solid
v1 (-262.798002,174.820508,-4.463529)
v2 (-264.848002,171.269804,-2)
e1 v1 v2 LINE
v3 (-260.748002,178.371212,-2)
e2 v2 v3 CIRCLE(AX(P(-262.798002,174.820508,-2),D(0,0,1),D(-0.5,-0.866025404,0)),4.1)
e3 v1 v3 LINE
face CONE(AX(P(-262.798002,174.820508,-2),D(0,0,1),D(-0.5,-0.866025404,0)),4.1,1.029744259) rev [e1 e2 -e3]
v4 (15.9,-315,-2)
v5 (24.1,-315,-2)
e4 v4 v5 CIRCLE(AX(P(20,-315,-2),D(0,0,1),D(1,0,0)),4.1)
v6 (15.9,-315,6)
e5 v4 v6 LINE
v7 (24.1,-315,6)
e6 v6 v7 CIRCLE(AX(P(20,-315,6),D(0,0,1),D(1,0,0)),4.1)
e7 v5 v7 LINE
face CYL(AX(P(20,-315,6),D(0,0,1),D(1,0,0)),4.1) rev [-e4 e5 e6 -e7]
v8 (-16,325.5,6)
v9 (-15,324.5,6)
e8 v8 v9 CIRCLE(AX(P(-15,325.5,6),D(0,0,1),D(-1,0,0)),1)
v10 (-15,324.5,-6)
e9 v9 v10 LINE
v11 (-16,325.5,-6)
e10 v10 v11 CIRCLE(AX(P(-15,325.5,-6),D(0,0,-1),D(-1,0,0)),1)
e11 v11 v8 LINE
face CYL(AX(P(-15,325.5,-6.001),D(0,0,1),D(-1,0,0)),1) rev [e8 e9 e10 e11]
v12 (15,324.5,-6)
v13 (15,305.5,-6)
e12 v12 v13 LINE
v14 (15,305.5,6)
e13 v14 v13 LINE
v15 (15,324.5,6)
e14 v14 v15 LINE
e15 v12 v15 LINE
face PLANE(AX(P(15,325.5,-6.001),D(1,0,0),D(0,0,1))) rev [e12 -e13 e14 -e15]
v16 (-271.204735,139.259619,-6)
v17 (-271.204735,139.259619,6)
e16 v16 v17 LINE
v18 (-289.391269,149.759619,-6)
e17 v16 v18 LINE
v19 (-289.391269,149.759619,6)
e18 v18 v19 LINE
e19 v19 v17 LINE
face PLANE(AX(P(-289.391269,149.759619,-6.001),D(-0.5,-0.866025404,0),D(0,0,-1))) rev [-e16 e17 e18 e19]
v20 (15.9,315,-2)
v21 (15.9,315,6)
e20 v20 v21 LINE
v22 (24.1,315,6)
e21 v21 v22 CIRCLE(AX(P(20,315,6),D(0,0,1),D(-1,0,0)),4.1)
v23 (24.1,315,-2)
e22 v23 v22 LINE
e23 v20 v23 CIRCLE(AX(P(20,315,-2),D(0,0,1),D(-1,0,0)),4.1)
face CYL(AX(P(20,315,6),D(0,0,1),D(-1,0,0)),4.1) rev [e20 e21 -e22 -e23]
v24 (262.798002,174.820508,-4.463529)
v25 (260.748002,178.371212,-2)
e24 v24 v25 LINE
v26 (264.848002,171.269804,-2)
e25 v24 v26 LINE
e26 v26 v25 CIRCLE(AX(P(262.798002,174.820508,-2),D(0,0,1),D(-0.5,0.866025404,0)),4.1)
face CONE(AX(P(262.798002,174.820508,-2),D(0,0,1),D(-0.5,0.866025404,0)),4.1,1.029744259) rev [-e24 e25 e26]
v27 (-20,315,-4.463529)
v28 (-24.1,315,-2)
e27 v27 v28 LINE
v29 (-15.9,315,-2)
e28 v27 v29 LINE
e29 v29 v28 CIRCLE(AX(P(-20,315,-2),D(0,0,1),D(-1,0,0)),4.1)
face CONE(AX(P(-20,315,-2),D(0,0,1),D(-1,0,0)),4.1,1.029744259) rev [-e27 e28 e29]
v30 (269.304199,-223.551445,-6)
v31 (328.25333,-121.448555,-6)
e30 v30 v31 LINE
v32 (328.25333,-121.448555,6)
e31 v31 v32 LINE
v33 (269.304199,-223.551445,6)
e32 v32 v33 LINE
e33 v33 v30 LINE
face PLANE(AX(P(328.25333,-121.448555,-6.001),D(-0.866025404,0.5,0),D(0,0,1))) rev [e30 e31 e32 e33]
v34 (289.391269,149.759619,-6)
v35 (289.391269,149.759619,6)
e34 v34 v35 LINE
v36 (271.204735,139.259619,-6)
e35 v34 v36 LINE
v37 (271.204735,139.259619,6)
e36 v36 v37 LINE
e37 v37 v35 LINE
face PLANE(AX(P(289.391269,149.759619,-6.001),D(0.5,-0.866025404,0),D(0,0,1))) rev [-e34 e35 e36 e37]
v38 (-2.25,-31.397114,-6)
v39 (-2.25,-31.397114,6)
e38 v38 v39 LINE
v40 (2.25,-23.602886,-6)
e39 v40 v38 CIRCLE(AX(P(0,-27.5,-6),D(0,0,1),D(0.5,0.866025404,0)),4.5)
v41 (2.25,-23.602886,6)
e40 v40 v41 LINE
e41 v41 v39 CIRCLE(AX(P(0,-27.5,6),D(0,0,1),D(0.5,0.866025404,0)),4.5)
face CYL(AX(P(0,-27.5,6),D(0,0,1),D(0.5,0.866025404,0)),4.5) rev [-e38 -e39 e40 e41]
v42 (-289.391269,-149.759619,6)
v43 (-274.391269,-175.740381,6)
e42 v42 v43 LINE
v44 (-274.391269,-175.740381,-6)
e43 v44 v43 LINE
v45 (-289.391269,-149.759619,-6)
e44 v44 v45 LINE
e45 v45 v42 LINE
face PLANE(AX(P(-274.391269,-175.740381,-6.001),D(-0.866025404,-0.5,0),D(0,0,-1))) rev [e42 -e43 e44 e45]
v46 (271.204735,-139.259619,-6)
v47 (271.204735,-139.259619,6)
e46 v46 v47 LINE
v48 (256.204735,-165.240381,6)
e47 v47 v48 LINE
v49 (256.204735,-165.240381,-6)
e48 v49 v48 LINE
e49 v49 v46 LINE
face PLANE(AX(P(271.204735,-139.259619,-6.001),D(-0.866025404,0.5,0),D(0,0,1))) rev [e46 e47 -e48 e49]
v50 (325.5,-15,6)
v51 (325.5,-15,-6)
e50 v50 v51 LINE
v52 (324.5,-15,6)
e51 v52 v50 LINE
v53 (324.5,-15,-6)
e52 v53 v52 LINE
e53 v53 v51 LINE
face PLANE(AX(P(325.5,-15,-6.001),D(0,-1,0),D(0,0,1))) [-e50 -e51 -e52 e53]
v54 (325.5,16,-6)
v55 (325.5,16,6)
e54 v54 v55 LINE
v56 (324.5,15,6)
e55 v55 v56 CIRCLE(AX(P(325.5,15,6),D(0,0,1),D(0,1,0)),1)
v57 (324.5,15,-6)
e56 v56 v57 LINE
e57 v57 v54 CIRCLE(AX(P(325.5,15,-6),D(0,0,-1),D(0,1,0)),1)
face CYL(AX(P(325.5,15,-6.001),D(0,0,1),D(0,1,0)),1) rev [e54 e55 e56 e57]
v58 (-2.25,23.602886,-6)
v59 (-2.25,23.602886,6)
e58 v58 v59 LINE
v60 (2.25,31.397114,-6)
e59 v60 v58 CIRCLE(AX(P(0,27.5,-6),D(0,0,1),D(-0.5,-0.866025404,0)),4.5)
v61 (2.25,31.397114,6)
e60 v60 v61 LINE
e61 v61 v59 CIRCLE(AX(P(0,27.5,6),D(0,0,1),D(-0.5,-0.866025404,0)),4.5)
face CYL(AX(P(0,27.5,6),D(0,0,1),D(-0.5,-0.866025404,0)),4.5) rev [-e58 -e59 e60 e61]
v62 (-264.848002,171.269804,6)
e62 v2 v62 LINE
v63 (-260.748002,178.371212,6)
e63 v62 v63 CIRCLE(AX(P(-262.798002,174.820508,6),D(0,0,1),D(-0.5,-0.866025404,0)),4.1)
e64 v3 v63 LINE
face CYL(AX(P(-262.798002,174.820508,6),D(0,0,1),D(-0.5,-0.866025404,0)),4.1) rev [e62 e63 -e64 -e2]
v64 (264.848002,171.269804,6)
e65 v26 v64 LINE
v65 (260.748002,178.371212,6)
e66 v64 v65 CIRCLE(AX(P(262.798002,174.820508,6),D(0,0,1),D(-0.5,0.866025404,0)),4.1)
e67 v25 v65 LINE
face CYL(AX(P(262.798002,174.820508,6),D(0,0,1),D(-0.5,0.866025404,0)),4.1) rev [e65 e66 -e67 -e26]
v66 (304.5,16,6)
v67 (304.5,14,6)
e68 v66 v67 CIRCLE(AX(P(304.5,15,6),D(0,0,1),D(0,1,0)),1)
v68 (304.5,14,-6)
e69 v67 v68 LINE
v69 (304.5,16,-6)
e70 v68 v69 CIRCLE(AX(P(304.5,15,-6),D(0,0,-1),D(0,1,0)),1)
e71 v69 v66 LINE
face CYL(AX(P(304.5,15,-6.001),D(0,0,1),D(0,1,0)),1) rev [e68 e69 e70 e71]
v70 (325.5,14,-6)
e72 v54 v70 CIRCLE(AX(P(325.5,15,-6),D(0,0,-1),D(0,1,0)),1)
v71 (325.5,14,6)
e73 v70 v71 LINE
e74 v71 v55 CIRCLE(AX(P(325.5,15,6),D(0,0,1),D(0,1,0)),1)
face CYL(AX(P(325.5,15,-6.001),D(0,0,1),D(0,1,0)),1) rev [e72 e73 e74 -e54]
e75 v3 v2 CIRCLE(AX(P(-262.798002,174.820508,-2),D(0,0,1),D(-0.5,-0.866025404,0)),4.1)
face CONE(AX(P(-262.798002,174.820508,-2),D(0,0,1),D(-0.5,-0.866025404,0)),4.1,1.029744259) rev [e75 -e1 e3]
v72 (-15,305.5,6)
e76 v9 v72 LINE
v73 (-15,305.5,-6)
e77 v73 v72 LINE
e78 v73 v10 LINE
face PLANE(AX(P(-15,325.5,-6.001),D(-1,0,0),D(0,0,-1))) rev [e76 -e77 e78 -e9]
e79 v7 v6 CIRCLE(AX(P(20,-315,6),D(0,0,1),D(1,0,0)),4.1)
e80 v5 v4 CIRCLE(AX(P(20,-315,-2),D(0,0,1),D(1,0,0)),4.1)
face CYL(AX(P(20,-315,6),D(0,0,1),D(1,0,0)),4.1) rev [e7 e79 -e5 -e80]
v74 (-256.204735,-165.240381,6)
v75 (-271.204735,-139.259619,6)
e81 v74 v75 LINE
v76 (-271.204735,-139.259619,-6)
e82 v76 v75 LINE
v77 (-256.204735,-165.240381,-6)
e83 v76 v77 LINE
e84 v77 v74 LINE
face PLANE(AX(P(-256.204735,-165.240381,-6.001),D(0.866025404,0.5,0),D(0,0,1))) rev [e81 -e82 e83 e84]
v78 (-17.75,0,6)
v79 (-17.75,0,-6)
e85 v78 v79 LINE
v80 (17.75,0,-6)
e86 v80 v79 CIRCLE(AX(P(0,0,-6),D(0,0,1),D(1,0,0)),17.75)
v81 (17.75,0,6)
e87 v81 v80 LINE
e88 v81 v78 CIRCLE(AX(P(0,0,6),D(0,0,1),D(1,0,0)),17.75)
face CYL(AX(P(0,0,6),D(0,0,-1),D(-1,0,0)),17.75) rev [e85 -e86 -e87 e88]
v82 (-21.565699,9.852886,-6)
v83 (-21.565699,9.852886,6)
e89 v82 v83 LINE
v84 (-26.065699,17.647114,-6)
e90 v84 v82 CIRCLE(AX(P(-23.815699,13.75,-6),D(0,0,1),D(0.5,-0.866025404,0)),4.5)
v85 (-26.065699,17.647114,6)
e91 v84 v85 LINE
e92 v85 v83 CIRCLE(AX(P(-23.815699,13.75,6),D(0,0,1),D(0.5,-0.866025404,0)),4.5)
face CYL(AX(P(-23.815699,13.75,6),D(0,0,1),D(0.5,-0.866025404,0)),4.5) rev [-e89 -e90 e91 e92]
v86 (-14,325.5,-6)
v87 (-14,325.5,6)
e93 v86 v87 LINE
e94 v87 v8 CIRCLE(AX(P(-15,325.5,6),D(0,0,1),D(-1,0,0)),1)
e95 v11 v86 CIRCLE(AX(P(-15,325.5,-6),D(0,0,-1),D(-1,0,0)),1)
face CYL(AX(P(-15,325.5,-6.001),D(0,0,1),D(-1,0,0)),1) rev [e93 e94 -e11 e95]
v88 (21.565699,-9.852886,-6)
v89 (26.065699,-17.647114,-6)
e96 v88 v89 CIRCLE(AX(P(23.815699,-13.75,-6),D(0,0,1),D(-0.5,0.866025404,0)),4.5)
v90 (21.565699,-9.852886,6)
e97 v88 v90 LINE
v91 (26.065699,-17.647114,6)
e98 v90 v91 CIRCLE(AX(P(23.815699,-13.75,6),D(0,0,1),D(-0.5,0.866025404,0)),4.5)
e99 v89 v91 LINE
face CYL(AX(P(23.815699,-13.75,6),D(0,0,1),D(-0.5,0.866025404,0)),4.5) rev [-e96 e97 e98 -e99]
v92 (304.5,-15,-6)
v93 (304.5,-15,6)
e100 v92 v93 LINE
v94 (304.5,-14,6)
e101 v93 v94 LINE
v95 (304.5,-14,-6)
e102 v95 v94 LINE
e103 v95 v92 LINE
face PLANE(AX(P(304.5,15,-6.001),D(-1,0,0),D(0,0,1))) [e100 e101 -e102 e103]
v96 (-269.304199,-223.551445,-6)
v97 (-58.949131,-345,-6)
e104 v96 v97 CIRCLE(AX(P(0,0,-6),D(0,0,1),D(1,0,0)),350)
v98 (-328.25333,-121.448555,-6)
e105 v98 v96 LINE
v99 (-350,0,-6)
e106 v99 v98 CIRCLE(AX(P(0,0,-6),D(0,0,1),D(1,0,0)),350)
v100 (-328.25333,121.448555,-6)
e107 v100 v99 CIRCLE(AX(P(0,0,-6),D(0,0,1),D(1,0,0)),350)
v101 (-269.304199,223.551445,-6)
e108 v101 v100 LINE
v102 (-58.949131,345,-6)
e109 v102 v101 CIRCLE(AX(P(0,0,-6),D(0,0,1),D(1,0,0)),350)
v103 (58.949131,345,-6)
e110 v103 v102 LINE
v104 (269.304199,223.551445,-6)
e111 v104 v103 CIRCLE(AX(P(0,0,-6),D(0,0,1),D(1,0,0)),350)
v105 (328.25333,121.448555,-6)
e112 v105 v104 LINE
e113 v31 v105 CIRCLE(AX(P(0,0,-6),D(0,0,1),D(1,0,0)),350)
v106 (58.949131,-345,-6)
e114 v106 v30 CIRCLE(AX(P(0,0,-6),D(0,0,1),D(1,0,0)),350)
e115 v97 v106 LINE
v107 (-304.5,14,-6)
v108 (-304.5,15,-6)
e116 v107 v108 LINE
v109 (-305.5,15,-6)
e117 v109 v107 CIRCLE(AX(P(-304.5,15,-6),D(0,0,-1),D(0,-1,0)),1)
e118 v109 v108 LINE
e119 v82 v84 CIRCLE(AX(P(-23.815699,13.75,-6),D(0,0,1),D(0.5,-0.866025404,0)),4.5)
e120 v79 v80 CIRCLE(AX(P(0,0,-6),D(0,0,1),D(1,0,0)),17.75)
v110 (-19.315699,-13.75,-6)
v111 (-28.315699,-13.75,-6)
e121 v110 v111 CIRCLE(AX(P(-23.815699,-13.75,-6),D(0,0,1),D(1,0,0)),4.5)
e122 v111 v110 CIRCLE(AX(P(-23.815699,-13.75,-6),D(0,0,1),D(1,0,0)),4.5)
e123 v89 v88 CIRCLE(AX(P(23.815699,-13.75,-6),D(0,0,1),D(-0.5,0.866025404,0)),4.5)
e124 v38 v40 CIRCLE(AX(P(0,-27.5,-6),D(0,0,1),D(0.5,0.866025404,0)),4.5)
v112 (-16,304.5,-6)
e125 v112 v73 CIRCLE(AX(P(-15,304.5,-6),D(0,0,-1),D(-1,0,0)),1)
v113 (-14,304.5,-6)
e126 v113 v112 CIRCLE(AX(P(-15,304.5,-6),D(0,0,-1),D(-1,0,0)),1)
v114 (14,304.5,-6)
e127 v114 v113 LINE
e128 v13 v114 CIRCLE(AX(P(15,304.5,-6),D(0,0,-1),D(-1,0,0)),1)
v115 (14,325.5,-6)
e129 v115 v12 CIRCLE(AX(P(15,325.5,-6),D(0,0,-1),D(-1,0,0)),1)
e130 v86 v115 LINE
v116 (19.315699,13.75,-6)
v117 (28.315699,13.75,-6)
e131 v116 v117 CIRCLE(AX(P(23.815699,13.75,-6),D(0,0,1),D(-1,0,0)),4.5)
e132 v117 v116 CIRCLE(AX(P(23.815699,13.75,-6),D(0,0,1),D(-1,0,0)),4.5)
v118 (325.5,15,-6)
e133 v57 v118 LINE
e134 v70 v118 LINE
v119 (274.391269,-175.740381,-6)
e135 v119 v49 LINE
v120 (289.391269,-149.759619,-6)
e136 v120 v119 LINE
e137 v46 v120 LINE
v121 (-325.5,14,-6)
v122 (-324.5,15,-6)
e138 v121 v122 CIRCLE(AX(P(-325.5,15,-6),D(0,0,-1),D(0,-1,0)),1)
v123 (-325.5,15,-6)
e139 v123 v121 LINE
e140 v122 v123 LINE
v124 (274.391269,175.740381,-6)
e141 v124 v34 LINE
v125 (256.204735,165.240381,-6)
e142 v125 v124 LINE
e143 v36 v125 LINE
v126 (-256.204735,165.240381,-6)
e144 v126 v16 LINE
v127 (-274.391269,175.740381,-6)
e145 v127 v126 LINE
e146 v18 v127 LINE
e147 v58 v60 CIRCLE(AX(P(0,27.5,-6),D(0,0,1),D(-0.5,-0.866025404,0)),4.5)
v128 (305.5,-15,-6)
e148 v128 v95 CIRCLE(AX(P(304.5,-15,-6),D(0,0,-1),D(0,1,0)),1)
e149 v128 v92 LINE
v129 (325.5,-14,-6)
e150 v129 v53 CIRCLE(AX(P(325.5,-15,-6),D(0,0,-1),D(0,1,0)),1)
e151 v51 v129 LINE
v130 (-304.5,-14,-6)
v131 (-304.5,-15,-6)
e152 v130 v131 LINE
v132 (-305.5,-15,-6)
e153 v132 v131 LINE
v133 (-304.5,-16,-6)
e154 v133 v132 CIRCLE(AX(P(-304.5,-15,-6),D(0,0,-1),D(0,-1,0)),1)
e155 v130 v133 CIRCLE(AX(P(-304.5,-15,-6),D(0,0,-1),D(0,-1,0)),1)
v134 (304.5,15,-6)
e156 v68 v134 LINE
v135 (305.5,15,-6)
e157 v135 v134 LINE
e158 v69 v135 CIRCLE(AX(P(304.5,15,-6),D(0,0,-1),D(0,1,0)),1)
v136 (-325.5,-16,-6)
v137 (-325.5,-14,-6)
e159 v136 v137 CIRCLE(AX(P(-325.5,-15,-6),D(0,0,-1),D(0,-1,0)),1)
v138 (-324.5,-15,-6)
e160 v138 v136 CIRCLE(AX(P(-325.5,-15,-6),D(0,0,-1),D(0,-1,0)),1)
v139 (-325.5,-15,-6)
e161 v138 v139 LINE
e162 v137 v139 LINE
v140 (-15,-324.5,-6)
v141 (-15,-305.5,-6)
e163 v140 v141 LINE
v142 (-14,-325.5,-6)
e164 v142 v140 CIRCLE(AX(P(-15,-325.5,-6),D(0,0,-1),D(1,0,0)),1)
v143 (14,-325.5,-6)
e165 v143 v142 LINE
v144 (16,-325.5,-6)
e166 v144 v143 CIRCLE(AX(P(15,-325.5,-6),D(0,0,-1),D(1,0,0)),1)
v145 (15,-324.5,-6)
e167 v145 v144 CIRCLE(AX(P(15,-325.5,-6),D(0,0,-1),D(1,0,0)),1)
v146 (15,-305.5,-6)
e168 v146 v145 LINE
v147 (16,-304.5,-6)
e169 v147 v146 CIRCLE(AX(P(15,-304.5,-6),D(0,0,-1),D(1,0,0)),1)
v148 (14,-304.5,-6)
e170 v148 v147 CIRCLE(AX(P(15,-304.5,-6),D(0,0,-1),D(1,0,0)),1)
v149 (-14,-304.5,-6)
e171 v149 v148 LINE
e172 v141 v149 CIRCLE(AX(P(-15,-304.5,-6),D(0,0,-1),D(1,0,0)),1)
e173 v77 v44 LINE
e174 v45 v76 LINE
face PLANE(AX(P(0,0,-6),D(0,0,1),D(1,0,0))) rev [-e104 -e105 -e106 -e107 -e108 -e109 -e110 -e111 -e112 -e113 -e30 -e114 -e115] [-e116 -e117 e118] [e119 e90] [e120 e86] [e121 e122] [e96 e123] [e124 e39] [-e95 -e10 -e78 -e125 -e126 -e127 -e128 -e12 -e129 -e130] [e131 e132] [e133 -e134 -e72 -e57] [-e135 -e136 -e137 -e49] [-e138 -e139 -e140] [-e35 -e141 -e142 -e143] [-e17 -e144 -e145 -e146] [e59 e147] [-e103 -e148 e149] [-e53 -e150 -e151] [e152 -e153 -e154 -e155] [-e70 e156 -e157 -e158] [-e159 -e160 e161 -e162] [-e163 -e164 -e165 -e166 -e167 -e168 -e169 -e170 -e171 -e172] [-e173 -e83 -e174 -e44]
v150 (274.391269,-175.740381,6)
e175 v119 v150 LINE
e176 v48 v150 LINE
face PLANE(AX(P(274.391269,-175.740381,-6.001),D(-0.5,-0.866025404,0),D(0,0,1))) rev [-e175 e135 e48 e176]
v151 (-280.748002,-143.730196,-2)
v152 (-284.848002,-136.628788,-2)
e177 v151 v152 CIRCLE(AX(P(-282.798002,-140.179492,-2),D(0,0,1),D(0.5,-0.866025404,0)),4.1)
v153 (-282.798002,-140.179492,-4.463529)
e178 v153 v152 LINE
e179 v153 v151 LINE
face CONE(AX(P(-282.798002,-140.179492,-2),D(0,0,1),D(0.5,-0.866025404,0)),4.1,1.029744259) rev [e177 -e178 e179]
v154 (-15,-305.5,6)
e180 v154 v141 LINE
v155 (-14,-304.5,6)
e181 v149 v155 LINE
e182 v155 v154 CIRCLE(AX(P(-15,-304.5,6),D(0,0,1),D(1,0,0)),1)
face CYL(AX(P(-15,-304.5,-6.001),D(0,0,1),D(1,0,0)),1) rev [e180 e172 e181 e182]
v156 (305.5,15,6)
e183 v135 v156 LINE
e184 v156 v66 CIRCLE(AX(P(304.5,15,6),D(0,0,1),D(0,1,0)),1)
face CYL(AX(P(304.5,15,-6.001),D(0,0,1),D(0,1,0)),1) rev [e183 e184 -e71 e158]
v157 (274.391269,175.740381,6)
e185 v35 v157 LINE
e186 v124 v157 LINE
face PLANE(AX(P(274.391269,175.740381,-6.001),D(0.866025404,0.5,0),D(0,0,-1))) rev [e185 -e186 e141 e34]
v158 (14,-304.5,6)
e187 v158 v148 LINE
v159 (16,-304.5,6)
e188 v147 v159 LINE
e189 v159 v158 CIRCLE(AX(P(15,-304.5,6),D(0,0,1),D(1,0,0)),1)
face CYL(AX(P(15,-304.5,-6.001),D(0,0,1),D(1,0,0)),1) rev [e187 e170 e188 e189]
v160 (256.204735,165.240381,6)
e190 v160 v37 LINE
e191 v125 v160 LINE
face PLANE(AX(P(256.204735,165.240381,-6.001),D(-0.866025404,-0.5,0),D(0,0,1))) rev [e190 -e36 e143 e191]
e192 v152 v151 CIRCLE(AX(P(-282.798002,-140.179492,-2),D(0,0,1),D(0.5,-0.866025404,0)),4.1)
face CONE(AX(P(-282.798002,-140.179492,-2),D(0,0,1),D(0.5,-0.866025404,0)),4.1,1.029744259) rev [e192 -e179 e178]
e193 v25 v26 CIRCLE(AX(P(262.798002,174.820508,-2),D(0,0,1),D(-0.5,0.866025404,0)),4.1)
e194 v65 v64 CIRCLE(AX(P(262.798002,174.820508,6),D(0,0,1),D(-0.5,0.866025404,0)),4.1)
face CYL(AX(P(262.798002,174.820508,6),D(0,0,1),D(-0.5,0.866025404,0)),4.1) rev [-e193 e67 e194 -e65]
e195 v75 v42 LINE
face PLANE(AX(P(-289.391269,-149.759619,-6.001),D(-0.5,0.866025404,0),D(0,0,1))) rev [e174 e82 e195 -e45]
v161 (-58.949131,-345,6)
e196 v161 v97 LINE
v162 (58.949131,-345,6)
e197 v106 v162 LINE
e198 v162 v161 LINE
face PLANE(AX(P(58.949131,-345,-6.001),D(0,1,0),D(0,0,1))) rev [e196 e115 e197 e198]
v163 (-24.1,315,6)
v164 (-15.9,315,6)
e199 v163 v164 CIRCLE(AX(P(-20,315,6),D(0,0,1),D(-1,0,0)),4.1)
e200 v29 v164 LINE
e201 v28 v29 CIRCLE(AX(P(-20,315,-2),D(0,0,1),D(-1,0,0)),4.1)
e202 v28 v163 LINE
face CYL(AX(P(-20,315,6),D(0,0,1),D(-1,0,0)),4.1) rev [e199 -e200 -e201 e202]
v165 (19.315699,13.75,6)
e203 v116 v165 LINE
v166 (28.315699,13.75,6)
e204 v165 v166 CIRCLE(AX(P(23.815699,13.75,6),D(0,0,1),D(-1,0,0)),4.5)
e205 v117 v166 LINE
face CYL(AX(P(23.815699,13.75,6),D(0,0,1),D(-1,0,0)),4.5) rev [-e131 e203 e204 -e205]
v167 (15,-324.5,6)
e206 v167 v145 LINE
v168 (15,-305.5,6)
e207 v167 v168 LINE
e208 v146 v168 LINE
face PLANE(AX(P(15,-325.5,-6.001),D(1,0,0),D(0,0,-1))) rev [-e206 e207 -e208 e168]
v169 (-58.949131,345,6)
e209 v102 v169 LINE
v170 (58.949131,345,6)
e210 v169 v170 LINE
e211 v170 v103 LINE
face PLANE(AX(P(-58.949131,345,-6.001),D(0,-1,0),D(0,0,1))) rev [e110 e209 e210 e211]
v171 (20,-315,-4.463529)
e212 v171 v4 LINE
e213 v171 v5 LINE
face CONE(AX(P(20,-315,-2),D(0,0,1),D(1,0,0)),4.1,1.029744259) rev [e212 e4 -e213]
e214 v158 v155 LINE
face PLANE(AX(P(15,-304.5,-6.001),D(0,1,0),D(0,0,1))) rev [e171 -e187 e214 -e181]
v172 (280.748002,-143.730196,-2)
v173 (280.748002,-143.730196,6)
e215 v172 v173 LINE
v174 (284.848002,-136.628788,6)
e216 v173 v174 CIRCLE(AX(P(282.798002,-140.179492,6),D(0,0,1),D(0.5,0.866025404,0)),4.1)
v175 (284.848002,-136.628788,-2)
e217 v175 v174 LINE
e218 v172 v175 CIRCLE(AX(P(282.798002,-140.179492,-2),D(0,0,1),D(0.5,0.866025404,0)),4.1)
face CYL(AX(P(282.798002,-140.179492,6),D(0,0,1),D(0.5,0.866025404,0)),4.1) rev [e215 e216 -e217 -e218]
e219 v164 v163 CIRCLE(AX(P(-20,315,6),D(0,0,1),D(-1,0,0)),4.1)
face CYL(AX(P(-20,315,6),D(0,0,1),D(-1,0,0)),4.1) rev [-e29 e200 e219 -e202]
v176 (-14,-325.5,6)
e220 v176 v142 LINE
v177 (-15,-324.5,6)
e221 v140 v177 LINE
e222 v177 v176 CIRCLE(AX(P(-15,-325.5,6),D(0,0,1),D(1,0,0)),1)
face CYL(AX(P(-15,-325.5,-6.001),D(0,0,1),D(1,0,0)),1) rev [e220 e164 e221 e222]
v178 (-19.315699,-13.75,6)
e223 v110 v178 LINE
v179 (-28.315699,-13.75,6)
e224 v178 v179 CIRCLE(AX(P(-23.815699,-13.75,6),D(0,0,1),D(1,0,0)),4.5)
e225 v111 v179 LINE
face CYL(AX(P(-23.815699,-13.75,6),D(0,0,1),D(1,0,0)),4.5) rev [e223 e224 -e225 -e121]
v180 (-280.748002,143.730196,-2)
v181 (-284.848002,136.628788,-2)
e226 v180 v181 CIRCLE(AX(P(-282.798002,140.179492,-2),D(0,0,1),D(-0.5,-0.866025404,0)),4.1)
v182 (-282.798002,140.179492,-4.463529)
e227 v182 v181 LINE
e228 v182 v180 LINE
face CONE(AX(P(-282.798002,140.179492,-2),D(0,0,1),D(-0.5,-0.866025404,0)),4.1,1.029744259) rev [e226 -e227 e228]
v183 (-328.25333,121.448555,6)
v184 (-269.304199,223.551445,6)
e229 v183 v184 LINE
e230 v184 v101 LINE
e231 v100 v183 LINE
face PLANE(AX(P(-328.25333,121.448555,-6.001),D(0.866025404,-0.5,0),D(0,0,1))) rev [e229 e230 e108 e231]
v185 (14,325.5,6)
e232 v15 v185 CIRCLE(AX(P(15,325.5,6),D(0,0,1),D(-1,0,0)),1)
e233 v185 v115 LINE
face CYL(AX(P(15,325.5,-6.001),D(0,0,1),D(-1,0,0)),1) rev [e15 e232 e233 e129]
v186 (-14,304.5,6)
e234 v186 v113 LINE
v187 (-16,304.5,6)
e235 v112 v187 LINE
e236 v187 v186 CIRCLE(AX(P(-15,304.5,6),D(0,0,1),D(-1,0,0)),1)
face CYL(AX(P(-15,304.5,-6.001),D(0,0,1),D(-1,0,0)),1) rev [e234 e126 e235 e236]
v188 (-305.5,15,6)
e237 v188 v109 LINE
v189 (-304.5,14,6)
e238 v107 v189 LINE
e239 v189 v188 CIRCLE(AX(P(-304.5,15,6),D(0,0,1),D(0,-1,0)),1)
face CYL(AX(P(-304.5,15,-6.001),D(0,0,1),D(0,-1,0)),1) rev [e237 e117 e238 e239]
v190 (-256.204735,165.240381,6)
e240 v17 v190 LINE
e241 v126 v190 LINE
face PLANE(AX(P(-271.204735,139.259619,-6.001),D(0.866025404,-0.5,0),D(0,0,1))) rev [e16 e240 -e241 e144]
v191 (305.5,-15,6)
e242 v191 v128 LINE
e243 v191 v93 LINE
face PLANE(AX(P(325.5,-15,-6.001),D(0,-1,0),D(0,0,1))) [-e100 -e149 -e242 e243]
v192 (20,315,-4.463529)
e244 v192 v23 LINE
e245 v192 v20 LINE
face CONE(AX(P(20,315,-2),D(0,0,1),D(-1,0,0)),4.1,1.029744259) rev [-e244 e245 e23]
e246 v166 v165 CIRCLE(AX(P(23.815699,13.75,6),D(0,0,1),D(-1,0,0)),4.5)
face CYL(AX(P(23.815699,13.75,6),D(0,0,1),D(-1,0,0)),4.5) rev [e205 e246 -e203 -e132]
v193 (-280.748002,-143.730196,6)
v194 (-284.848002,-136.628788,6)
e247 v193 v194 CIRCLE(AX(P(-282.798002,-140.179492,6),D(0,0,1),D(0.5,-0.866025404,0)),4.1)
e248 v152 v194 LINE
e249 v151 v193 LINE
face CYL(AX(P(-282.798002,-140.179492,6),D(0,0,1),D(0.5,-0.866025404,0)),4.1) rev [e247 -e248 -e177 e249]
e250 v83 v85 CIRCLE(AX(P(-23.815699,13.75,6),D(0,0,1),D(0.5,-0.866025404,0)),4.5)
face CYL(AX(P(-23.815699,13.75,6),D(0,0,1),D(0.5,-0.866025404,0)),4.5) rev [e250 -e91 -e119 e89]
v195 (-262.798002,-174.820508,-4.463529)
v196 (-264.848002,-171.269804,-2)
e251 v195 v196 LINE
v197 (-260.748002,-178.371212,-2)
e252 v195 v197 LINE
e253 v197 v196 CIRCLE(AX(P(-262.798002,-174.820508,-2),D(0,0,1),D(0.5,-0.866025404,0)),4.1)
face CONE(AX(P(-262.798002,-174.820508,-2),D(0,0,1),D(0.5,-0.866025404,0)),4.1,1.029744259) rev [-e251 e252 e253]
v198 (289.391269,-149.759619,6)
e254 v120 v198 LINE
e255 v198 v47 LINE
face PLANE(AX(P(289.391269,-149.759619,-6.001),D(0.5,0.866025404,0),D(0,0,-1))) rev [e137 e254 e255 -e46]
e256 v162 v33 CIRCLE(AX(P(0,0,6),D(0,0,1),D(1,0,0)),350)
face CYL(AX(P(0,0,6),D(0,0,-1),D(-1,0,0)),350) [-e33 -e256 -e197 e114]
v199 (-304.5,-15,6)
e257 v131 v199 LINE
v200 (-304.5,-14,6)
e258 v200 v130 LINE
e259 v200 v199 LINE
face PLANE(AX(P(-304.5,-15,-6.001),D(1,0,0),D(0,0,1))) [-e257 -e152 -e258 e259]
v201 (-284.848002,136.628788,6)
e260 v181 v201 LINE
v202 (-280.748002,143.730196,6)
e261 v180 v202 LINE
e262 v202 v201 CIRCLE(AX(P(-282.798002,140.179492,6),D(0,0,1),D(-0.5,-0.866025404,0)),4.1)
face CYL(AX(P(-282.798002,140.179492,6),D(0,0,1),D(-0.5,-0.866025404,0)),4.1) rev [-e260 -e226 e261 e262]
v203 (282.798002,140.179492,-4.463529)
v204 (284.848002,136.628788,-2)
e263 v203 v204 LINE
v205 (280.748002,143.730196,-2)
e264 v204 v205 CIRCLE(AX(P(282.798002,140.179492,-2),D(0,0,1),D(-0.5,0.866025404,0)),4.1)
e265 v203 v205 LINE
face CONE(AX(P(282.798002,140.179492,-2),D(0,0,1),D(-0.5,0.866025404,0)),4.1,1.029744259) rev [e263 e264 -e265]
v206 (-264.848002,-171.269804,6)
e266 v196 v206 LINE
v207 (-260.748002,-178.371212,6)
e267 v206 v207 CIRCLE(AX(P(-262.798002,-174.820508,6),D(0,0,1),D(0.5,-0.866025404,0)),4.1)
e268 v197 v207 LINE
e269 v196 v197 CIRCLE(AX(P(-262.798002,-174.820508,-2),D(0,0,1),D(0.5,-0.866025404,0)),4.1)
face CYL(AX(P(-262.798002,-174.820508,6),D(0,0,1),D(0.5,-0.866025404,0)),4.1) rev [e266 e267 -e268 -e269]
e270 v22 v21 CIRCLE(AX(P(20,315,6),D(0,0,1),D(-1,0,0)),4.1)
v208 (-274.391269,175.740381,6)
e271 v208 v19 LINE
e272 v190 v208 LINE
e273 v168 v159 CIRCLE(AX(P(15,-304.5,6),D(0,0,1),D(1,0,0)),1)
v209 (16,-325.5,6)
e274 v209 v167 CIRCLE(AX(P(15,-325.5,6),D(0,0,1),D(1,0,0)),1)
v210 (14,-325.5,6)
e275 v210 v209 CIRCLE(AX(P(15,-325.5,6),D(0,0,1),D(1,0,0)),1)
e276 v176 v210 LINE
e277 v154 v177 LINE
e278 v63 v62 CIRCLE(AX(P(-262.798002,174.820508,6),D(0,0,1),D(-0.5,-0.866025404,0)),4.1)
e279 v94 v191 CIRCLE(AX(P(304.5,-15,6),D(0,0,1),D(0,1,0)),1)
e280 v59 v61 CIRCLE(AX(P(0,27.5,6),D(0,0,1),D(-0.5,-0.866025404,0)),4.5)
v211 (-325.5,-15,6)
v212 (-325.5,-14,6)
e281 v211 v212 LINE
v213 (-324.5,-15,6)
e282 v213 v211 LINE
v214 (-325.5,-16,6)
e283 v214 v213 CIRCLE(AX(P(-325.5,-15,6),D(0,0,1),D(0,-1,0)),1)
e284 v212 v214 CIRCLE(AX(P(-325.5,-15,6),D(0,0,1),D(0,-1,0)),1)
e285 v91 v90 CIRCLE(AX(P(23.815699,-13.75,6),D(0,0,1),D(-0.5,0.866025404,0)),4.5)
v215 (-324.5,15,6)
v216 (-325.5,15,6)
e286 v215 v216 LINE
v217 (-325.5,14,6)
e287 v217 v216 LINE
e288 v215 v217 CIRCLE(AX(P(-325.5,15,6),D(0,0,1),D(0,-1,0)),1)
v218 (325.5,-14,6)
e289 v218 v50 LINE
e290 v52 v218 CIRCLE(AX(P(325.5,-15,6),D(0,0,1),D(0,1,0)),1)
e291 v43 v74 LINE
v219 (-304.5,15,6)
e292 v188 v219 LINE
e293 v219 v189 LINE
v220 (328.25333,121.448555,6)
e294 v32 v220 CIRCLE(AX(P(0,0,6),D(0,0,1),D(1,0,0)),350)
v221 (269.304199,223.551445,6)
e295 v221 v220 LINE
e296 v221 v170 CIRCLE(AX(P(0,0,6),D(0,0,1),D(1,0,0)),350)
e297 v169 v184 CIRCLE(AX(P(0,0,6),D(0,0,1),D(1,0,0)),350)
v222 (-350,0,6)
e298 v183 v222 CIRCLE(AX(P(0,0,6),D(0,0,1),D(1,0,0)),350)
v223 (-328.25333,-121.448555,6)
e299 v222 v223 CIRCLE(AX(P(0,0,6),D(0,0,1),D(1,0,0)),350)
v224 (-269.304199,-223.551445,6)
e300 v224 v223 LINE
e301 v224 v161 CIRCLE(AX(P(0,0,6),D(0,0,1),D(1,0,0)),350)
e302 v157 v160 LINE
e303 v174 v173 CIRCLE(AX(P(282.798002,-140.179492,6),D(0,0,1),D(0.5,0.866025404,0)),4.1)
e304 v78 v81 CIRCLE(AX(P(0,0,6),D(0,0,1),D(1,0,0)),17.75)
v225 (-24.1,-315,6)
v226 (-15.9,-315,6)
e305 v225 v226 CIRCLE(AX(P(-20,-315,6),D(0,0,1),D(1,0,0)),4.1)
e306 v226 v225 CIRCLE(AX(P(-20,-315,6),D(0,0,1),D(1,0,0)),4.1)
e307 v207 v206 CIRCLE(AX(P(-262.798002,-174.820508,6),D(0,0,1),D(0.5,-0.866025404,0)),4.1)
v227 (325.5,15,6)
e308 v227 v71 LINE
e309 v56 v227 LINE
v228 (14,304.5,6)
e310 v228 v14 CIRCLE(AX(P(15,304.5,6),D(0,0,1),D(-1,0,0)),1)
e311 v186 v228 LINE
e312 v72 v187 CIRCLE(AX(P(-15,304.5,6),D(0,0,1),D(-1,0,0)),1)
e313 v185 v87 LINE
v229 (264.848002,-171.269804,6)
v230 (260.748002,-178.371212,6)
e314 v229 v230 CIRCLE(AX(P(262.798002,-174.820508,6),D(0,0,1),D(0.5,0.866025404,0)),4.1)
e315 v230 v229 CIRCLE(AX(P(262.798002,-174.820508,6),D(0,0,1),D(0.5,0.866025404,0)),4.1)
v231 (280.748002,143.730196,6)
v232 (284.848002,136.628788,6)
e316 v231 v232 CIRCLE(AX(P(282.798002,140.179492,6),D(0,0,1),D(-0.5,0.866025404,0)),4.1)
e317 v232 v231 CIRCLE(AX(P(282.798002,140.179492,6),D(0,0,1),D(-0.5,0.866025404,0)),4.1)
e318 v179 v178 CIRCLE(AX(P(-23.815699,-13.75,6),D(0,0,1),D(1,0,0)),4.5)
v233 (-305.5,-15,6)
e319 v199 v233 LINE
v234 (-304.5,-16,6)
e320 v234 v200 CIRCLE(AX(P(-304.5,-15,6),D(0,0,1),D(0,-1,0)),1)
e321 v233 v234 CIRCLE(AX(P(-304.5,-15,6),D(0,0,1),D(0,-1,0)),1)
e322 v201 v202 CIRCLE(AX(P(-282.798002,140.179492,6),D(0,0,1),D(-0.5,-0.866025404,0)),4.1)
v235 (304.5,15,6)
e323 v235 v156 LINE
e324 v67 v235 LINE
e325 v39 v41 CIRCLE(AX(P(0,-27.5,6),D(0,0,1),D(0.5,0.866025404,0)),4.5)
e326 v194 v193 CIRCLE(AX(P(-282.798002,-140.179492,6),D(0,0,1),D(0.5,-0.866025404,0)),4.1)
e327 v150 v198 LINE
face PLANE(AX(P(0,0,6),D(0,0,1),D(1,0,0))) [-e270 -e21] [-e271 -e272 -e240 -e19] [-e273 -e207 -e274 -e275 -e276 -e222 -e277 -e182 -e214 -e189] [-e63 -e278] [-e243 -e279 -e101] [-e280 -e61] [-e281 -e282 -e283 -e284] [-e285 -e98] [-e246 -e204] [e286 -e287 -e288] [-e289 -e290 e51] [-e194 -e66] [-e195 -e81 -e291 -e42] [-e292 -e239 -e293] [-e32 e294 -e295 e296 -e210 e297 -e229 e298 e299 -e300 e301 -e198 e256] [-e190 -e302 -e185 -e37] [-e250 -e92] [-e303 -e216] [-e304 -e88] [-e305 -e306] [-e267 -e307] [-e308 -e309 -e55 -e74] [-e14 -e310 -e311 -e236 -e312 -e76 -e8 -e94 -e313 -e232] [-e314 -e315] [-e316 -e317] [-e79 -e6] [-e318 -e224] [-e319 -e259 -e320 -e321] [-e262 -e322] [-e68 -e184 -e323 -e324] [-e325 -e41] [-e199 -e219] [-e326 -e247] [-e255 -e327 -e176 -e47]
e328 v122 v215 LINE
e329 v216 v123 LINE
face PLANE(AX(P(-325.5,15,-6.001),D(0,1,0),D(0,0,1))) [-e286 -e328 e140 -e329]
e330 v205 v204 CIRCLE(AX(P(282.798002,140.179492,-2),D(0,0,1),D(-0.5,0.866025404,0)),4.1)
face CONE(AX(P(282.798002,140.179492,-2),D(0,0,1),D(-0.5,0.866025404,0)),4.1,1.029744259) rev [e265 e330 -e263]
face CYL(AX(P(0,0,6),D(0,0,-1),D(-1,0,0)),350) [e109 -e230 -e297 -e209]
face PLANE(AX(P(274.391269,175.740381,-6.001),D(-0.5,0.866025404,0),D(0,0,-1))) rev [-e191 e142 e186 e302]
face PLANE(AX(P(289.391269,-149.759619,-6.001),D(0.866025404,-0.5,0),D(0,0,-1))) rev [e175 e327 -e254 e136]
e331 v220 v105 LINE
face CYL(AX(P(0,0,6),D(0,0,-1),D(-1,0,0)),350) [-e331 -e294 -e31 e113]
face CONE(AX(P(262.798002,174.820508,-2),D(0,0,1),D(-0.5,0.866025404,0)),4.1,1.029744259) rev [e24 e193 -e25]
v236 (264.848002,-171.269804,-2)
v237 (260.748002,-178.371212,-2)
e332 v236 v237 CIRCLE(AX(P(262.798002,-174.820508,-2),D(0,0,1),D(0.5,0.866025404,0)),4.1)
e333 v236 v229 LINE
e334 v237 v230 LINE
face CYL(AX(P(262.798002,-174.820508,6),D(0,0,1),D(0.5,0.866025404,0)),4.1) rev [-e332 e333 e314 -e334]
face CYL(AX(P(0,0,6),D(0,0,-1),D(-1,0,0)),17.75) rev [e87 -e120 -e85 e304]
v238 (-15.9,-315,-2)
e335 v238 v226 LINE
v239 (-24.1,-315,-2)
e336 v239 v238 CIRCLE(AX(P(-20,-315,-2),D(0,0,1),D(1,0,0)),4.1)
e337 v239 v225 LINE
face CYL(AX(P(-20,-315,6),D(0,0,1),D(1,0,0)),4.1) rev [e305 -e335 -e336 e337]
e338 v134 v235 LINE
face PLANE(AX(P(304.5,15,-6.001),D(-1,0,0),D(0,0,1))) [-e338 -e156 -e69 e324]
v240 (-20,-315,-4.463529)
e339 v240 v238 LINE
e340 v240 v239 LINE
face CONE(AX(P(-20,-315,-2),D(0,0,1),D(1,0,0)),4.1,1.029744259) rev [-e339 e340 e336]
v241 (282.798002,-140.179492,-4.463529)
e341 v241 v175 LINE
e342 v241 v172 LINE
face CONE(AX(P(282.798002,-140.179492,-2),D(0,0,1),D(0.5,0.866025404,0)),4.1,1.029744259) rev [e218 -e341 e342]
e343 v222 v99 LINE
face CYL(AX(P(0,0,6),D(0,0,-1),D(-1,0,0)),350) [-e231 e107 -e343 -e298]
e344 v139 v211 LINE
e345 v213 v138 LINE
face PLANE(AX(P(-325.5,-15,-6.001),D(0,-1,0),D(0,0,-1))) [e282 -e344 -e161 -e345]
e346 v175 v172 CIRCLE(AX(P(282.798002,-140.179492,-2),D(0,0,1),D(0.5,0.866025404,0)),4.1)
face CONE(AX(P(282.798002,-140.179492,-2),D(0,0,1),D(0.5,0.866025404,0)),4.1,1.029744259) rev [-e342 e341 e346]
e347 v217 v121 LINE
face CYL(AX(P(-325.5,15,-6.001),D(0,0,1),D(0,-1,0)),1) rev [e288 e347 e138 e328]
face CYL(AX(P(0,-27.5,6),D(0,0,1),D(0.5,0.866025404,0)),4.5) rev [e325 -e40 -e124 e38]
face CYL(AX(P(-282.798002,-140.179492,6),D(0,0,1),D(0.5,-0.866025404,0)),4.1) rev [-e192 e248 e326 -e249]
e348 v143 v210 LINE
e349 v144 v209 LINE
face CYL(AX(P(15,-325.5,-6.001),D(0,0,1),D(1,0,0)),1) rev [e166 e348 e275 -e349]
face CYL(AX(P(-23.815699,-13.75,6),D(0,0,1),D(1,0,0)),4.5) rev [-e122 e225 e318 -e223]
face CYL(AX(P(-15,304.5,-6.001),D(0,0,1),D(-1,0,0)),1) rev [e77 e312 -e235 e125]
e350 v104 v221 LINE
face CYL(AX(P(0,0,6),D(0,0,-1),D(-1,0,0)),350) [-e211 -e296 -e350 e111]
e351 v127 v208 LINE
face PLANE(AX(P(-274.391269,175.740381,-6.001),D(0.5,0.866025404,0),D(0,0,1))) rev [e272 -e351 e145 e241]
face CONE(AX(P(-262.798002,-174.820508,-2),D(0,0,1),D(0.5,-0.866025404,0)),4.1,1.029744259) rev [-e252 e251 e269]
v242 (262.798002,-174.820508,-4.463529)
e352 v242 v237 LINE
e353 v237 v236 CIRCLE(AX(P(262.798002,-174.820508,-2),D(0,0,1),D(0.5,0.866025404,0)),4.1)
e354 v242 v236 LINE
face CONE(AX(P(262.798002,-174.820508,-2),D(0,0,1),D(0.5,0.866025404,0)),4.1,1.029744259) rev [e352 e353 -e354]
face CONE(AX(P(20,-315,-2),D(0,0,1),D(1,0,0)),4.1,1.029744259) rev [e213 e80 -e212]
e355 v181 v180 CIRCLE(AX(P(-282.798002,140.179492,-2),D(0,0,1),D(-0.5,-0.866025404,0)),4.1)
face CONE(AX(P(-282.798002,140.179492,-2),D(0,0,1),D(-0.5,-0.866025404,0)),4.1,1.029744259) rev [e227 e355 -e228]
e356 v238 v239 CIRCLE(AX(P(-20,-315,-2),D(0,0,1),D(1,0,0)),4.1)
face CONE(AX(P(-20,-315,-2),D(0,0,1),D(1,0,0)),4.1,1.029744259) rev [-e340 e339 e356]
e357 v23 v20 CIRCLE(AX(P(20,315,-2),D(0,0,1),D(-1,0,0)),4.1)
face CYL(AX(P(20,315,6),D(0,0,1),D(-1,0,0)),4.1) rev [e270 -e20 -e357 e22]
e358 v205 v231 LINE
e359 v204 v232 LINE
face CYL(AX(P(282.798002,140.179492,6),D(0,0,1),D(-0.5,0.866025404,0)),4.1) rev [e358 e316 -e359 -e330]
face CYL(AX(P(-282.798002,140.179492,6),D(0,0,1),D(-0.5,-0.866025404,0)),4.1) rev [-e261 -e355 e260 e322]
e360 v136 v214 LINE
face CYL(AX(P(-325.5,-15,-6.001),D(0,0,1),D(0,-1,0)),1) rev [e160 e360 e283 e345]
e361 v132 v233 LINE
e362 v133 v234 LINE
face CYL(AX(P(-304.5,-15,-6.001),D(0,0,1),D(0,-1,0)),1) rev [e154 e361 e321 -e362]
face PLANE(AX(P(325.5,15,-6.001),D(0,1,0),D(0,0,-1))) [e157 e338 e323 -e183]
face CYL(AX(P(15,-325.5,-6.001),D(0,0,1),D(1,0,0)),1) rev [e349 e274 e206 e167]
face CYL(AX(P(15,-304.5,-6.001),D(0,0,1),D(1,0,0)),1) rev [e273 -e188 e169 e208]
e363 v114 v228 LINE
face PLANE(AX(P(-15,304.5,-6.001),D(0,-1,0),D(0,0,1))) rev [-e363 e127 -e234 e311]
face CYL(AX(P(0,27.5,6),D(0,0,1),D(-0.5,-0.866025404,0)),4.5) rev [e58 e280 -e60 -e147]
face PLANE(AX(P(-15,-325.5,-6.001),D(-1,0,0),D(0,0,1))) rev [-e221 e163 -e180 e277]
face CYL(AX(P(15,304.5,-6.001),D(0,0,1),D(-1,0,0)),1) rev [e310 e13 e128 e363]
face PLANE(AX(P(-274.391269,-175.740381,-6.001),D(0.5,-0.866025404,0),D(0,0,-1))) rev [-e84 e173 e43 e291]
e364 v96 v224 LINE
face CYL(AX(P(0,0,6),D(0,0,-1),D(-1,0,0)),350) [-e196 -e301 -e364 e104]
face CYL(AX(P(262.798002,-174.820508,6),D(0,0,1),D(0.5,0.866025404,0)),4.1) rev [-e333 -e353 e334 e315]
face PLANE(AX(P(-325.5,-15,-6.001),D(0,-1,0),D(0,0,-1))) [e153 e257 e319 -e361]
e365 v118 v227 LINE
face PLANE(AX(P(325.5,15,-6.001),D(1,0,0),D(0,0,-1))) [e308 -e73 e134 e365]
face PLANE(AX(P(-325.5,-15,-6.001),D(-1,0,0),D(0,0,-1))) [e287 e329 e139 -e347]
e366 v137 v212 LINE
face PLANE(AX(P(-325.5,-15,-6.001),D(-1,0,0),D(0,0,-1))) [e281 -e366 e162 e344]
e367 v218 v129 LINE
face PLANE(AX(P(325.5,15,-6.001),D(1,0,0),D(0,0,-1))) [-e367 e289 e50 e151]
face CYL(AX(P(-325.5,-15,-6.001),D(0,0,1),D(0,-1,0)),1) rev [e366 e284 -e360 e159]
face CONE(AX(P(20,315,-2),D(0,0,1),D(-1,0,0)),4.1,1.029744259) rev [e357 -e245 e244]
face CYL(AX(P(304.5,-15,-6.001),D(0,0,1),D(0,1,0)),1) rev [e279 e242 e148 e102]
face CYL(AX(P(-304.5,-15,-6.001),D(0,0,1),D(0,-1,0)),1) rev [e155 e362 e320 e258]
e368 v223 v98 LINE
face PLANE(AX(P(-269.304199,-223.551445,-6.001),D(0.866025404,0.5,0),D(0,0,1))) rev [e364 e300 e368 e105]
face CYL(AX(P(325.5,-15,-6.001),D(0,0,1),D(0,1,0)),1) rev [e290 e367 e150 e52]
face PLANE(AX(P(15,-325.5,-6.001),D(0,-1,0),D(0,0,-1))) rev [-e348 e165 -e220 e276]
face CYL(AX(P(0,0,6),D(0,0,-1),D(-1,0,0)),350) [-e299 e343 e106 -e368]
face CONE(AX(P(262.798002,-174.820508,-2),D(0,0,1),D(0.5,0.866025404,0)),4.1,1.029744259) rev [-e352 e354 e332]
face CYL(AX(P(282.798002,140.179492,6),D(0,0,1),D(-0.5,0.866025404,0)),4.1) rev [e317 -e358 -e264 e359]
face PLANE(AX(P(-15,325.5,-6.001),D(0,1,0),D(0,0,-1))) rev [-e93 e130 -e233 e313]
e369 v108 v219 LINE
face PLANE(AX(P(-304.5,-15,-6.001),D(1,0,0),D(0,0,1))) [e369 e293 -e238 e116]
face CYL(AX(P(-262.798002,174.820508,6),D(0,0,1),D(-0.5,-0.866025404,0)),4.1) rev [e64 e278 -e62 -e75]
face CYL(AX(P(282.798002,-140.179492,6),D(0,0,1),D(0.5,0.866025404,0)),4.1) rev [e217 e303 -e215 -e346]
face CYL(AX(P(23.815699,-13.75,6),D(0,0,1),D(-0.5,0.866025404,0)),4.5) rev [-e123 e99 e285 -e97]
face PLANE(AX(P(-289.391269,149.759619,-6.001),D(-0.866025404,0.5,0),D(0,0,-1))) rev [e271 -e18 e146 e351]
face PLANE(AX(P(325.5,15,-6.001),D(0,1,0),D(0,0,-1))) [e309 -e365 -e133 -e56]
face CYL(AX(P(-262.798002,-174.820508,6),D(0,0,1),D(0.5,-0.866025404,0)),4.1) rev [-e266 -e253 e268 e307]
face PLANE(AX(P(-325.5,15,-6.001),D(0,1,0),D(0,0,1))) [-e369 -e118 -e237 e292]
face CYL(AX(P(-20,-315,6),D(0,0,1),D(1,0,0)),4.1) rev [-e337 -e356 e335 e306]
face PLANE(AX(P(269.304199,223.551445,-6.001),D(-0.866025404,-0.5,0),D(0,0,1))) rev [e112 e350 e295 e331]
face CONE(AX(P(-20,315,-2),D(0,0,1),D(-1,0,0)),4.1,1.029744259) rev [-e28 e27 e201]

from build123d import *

# Parameters (mm, degrees)
SKETCH_1_R                       = 350
SKETCH_1_R_2                     = 17.75
EXTRUDE_1_DEPTH                  = 6
CUT_EXTRUDE_1_REACH              = 497.12
SKETCH_2_W                       = 117.898261226
SKETCH_2_H                       = 10
PATTERN_CIRCULAR_1_COUNT         = 6
CUT_EXTRUDE_2_REACH              = 493.598
SKETCH_3_W                       = 30
SKETCH_3_H                       = 21
PATTERN_CIRCULAR_2_COUNT         = 6
HOLE_WIZARD_M8_1_D               = 9
PATTERN_CIRCULAR_3_COUNT         = 6
HOLE_WIZARD_8_2_8_2_1_AT_2_COUNT = 2
HOLE_WIZARD_8_2_8_2_1_AT_2_PITCH = 40
PATTERN_CIRCULAR_5_COUNT         = 6
CUT_EXTRUDE_3_REACH              = 493.598
SKETCH_15_R                      = 1
PATTERN_CIRCULAR_6_COUNT         = 4


with BuildPart() as part:
    # 草图1 → 凸台-拉伸1 (new, symmetric)
    with BuildSketch(Plane.XY):
        Circle(SKETCH_1_R)
        Circle(SKETCH_1_R_2, mode=Mode.SUBTRACT)
    extrude(amount=EXTRUDE_1_DEPTH, both=True)

    # 草图2 → 切除-拉伸1 (cut, up to next)
    with BuildSketch(Plane.XY.offset(6), mode=Mode.PRIVATE) as cut_extrude_1_sk1:
        with Locations((0, -350)):
            Rectangle(SKETCH_2_W, SKETCH_2_H)
    cut_extrude_1_tool1 = extrude(cut_extrude_1_sk1.sketch, amount=-CUT_EXTRUDE_1_REACH, mode=Mode.PRIVATE) & part.part
    cut_extrude_1 = cut_extrude_1_tool1.solids().sort_by_distance((0, -350, 6))[0]
    add(cut_extrude_1, mode=Mode.SUBTRACT)

    # 阵列(圆周)1: 切除-拉伸1 ×6 about axis
    pattern_circular_1_axis = Axis((0, 0, 0), (0, 0, 1))
    for i in range(1, PATTERN_CIRCULAR_1_COUNT):
        add(cut_extrude_1.rotate(pattern_circular_1_axis, i * 360 / PATTERN_CIRCULAR_1_COUNT), mode=Mode.SUBTRACT)

    # 草图3 → 切除-拉伸2 (cut, up to next)
    with BuildSketch(Plane.XY.offset(6), mode=Mode.PRIVATE) as cut_extrude_2_sk1:
        with Locations((0, -315)):
            Rectangle(SKETCH_3_W, SKETCH_3_H)
    cut_extrude_2_tool1 = extrude(cut_extrude_2_sk1.sketch, amount=-CUT_EXTRUDE_2_REACH, mode=Mode.PRIVATE) & part.part
    cut_extrude_2 = cut_extrude_2_tool1.solids().sort_by_distance((0, -315, 6))[0]
    add(cut_extrude_2, mode=Mode.SUBTRACT)

    # 阵列(圆周)2: 切除-拉伸2 ×6 about axis
    pattern_circular_2_axis = Axis((0, 0, 0), (0, 0, 1))
    for i in range(1, PATTERN_CIRCULAR_2_COUNT):
        add(cut_extrude_2.rotate(pattern_circular_2_axis, i * 360 / PATTERN_CIRCULAR_2_COUNT), mode=Mode.SUBTRACT)

    # M8 间隙孔1 (through all)
    with Locations(Plane.XY.offset(6)):
        with Locations((-23.815698604, -13.75)):
            hole_wizard_m8_1 = Hole(HOLE_WIZARD_M8_1_D / 2)

    # 阵列(圆周)3: M8 间隙孔1 ×6 about axis
    pattern_circular_3_axis = Axis((0, 0, 0), (0, 0, 1))
    for i in range(1, PATTERN_CIRCULAR_3_COUNT):
        add(hole_wizard_m8_1.rotate(pattern_circular_3_axis, i * 360 / PATTERN_CIRCULAR_3_COUNT), mode=Mode.SUBTRACT)

    # 草图14 → Ø8.2 (8.2) 直径孔1 (revolve, cut)
    with BuildSketch(Plane(origin=(-20, -315, 6), x_dir=(0, -1, 0), z_dir=(1, 0, 0))):
        Polygon((0, 0), (0, 10.463528538), (4.1, 8), (4.1, 0), align=None)
    hole_wizard_8_2_8_2_1 = revolve(axis=Axis((-20, -315, 12.35), (0, 0, -1)), mode=Mode.SUBTRACT)

    # Ø8.2 (8.2) 直径孔1 at 2: Ø8.2 (8.2) 直径孔1 ×2
    with Locations(*[(i * HOLE_WIZARD_8_2_8_2_1_AT_2_PITCH, 0, 0) for i in range(1, HOLE_WIZARD_8_2_8_2_1_AT_2_COUNT)]):
        add(hole_wizard_8_2_8_2_1, mode=Mode.SUBTRACT)

    # 阵列(圆周)5: Ø8.2 (8.2) 直径孔1 ×6 about axis
    pattern_circular_5_axis = Axis((0, 0, 0), (0, 0, 1))
    for i in range(1, PATTERN_CIRCULAR_5_COUNT):
        add(hole_wizard_8_2_8_2_1.rotate(pattern_circular_5_axis, i * 360 / PATTERN_CIRCULAR_5_COUNT), mode=Mode.SUBTRACT)

    # 阵列(圆周)5 copy 1 sketch → 阵列(圆周)5 copy 1 (revolve, cut)
    with BuildSketch(Plane(origin=(282.798002192, -140.179491924, 6), x_dir=(0.8660254037844386, -0.5000000000000001, 0), z_dir=(0.5000000000000001, 0.8660254037844386, 0))):
        Polygon((0, 0), (0, 10.463528538), (4.1, 8), (4.1, 0), align=None)
    revolve(axis=Axis((282.798002192, -140.179491924, 12.35), (0, 0, -1)), mode=Mode.SUBTRACT)

    # 阵列(圆周)5 copy 2 sketch → 阵列(圆周)5 copy 2 (revolve, cut)
    with BuildSketch(Plane(origin=(262.798002192, 174.820508076, 6), x_dir=(0.8660254037844387, 0.4999999999999998, 0), z_dir=(-0.4999999999999998, 0.8660254037844387, 0))):
        Polygon((0, 0), (0, 10.463528538), (4.1, 8), (4.1, 0), align=None)
    revolve(axis=Axis((262.798002192, 174.820508076, 12.35), (0, 0, -1)), mode=Mode.SUBTRACT)

    # 阵列(圆周)5 copy 3 sketch → 阵列(圆周)5 copy 3 (revolve, cut)
    with BuildSketch(Plane(origin=(-20, 315, 6), x_dir=(0, 1, 0), z_dir=(-1, 0, 0))):
        Polygon((0, 0), (0, 10.463528538), (4.1, 8), (4.1, 0), align=None)
    revolve(axis=Axis((-20, 315, 12.35), (0, 0, -1)), mode=Mode.SUBTRACT)

    # 阵列(圆周)5 copy 4 sketch → 阵列(圆周)5 copy 4 (revolve, cut)
    with BuildSketch(Plane(origin=(-282.798002192, 140.179491924, 6), x_dir=(-0.8660254037844384, 0.5000000000000004, 0), z_dir=(-0.5000000000000004, -0.8660254037844384, 0))):
        Polygon((0, 0), (0, 10.463528538), (4.1, 8), (4.1, 0), align=None)
    revolve(axis=Axis((-282.798002192, 140.179491924, 12.35), (0, 0, -1)), mode=Mode.SUBTRACT)

    # 阵列(圆周)5 copy 5 sketch → 阵列(圆周)5 copy 5 (revolve, cut)
    with BuildSketch(Plane(origin=(-262.798002192, -174.820508076, 6), x_dir=(-0.8660254037844386, -0.5000000000000001, 0), z_dir=(0.5000000000000001, -0.8660254037844386, 0))):
        Polygon((0, 0), (0, 10.463528538), (4.1, 8), (4.1, 0), align=None)
    revolve(axis=Axis((-262.798002192, -174.820508076, 12.35), (0, 0, -1)), mode=Mode.SUBTRACT)

    # 草图15 → 切除-拉伸3 (cut, up to next)
    with BuildSketch(Plane.XY.offset(6), mode=Mode.PRIVATE) as cut_extrude_3_sk1:
        with Locations((-15, -325.5)):
            Circle(SKETCH_15_R)
    cut_extrude_3_tool1 = extrude(cut_extrude_3_sk1.sketch, amount=-CUT_EXTRUDE_3_REACH, mode=Mode.PRIVATE) & part.part
    # 草图15 → 切除-拉伸3 (cut, up to next)
    with BuildSketch(Plane.XY.offset(6), mode=Mode.PRIVATE) as cut_extrude_3_sk2:
        with Locations((15, -325.5)):
            Circle(SKETCH_15_R)
    cut_extrude_3_tool2 = extrude(cut_extrude_3_sk2.sketch, amount=-CUT_EXTRUDE_3_REACH, mode=Mode.PRIVATE) & part.part
    # 草图15 → 切除-拉伸3 (cut, up to next)
    with BuildSketch(Plane.XY.offset(6), mode=Mode.PRIVATE) as cut_extrude_3_sk3:
        with Locations((-15, -304.5)):
            Circle(SKETCH_15_R)
    cut_extrude_3_tool3 = extrude(cut_extrude_3_sk3.sketch, amount=-CUT_EXTRUDE_3_REACH, mode=Mode.PRIVATE) & part.part
    # 草图15 → 切除-拉伸3 (cut, up to next)
    with BuildSketch(Plane.XY.offset(6), mode=Mode.PRIVATE) as cut_extrude_3_sk4:
        with Locations((15, -304.5)):
            Circle(SKETCH_15_R)
    cut_extrude_3_tool4 = extrude(cut_extrude_3_sk4.sketch, amount=-CUT_EXTRUDE_3_REACH, mode=Mode.PRIVATE) & part.part
    cut_extrude_3_1 = cut_extrude_3_tool1.solids().sort_by_distance((-15, -325.5, 6))[0]
    add(cut_extrude_3_1, mode=Mode.SUBTRACT)
    cut_extrude_3_2 = cut_extrude_3_tool2.solids().sort_by_distance((15, -325.5, 6))[0]
    add(cut_extrude_3_2, mode=Mode.SUBTRACT)
    cut_extrude_3_3 = cut_extrude_3_tool3.solids().sort_by_distance((-15, -304.5, 6))[0]
    add(cut_extrude_3_3, mode=Mode.SUBTRACT)
    cut_extrude_3_4 = cut_extrude_3_tool4.solids().sort_by_distance((15, -304.5, 6))[0]
    add(cut_extrude_3_4, mode=Mode.SUBTRACT)
    cut_extrude_3 = cut_extrude_3_1 + cut_extrude_3_2 + cut_extrude_3_3 + cut_extrude_3_4  # 切除-拉伸3 as one shape, for the pattern or mirror that repeats it

    # 阵列(圆周)6: 切除-拉伸3 ×4 about axis
    pattern_circular_6_axis = Axis((0, 0, 0), (0, 0, 1))
    for i in range(1, PATTERN_CIRCULAR_6_COUNT):
        add(cut_extrude_3.rotate(pattern_circular_6_axis, i * 360 / PATTERN_CIRCULAR_6_COUNT), mode=Mode.SUBTRACT)


solid = part.part
